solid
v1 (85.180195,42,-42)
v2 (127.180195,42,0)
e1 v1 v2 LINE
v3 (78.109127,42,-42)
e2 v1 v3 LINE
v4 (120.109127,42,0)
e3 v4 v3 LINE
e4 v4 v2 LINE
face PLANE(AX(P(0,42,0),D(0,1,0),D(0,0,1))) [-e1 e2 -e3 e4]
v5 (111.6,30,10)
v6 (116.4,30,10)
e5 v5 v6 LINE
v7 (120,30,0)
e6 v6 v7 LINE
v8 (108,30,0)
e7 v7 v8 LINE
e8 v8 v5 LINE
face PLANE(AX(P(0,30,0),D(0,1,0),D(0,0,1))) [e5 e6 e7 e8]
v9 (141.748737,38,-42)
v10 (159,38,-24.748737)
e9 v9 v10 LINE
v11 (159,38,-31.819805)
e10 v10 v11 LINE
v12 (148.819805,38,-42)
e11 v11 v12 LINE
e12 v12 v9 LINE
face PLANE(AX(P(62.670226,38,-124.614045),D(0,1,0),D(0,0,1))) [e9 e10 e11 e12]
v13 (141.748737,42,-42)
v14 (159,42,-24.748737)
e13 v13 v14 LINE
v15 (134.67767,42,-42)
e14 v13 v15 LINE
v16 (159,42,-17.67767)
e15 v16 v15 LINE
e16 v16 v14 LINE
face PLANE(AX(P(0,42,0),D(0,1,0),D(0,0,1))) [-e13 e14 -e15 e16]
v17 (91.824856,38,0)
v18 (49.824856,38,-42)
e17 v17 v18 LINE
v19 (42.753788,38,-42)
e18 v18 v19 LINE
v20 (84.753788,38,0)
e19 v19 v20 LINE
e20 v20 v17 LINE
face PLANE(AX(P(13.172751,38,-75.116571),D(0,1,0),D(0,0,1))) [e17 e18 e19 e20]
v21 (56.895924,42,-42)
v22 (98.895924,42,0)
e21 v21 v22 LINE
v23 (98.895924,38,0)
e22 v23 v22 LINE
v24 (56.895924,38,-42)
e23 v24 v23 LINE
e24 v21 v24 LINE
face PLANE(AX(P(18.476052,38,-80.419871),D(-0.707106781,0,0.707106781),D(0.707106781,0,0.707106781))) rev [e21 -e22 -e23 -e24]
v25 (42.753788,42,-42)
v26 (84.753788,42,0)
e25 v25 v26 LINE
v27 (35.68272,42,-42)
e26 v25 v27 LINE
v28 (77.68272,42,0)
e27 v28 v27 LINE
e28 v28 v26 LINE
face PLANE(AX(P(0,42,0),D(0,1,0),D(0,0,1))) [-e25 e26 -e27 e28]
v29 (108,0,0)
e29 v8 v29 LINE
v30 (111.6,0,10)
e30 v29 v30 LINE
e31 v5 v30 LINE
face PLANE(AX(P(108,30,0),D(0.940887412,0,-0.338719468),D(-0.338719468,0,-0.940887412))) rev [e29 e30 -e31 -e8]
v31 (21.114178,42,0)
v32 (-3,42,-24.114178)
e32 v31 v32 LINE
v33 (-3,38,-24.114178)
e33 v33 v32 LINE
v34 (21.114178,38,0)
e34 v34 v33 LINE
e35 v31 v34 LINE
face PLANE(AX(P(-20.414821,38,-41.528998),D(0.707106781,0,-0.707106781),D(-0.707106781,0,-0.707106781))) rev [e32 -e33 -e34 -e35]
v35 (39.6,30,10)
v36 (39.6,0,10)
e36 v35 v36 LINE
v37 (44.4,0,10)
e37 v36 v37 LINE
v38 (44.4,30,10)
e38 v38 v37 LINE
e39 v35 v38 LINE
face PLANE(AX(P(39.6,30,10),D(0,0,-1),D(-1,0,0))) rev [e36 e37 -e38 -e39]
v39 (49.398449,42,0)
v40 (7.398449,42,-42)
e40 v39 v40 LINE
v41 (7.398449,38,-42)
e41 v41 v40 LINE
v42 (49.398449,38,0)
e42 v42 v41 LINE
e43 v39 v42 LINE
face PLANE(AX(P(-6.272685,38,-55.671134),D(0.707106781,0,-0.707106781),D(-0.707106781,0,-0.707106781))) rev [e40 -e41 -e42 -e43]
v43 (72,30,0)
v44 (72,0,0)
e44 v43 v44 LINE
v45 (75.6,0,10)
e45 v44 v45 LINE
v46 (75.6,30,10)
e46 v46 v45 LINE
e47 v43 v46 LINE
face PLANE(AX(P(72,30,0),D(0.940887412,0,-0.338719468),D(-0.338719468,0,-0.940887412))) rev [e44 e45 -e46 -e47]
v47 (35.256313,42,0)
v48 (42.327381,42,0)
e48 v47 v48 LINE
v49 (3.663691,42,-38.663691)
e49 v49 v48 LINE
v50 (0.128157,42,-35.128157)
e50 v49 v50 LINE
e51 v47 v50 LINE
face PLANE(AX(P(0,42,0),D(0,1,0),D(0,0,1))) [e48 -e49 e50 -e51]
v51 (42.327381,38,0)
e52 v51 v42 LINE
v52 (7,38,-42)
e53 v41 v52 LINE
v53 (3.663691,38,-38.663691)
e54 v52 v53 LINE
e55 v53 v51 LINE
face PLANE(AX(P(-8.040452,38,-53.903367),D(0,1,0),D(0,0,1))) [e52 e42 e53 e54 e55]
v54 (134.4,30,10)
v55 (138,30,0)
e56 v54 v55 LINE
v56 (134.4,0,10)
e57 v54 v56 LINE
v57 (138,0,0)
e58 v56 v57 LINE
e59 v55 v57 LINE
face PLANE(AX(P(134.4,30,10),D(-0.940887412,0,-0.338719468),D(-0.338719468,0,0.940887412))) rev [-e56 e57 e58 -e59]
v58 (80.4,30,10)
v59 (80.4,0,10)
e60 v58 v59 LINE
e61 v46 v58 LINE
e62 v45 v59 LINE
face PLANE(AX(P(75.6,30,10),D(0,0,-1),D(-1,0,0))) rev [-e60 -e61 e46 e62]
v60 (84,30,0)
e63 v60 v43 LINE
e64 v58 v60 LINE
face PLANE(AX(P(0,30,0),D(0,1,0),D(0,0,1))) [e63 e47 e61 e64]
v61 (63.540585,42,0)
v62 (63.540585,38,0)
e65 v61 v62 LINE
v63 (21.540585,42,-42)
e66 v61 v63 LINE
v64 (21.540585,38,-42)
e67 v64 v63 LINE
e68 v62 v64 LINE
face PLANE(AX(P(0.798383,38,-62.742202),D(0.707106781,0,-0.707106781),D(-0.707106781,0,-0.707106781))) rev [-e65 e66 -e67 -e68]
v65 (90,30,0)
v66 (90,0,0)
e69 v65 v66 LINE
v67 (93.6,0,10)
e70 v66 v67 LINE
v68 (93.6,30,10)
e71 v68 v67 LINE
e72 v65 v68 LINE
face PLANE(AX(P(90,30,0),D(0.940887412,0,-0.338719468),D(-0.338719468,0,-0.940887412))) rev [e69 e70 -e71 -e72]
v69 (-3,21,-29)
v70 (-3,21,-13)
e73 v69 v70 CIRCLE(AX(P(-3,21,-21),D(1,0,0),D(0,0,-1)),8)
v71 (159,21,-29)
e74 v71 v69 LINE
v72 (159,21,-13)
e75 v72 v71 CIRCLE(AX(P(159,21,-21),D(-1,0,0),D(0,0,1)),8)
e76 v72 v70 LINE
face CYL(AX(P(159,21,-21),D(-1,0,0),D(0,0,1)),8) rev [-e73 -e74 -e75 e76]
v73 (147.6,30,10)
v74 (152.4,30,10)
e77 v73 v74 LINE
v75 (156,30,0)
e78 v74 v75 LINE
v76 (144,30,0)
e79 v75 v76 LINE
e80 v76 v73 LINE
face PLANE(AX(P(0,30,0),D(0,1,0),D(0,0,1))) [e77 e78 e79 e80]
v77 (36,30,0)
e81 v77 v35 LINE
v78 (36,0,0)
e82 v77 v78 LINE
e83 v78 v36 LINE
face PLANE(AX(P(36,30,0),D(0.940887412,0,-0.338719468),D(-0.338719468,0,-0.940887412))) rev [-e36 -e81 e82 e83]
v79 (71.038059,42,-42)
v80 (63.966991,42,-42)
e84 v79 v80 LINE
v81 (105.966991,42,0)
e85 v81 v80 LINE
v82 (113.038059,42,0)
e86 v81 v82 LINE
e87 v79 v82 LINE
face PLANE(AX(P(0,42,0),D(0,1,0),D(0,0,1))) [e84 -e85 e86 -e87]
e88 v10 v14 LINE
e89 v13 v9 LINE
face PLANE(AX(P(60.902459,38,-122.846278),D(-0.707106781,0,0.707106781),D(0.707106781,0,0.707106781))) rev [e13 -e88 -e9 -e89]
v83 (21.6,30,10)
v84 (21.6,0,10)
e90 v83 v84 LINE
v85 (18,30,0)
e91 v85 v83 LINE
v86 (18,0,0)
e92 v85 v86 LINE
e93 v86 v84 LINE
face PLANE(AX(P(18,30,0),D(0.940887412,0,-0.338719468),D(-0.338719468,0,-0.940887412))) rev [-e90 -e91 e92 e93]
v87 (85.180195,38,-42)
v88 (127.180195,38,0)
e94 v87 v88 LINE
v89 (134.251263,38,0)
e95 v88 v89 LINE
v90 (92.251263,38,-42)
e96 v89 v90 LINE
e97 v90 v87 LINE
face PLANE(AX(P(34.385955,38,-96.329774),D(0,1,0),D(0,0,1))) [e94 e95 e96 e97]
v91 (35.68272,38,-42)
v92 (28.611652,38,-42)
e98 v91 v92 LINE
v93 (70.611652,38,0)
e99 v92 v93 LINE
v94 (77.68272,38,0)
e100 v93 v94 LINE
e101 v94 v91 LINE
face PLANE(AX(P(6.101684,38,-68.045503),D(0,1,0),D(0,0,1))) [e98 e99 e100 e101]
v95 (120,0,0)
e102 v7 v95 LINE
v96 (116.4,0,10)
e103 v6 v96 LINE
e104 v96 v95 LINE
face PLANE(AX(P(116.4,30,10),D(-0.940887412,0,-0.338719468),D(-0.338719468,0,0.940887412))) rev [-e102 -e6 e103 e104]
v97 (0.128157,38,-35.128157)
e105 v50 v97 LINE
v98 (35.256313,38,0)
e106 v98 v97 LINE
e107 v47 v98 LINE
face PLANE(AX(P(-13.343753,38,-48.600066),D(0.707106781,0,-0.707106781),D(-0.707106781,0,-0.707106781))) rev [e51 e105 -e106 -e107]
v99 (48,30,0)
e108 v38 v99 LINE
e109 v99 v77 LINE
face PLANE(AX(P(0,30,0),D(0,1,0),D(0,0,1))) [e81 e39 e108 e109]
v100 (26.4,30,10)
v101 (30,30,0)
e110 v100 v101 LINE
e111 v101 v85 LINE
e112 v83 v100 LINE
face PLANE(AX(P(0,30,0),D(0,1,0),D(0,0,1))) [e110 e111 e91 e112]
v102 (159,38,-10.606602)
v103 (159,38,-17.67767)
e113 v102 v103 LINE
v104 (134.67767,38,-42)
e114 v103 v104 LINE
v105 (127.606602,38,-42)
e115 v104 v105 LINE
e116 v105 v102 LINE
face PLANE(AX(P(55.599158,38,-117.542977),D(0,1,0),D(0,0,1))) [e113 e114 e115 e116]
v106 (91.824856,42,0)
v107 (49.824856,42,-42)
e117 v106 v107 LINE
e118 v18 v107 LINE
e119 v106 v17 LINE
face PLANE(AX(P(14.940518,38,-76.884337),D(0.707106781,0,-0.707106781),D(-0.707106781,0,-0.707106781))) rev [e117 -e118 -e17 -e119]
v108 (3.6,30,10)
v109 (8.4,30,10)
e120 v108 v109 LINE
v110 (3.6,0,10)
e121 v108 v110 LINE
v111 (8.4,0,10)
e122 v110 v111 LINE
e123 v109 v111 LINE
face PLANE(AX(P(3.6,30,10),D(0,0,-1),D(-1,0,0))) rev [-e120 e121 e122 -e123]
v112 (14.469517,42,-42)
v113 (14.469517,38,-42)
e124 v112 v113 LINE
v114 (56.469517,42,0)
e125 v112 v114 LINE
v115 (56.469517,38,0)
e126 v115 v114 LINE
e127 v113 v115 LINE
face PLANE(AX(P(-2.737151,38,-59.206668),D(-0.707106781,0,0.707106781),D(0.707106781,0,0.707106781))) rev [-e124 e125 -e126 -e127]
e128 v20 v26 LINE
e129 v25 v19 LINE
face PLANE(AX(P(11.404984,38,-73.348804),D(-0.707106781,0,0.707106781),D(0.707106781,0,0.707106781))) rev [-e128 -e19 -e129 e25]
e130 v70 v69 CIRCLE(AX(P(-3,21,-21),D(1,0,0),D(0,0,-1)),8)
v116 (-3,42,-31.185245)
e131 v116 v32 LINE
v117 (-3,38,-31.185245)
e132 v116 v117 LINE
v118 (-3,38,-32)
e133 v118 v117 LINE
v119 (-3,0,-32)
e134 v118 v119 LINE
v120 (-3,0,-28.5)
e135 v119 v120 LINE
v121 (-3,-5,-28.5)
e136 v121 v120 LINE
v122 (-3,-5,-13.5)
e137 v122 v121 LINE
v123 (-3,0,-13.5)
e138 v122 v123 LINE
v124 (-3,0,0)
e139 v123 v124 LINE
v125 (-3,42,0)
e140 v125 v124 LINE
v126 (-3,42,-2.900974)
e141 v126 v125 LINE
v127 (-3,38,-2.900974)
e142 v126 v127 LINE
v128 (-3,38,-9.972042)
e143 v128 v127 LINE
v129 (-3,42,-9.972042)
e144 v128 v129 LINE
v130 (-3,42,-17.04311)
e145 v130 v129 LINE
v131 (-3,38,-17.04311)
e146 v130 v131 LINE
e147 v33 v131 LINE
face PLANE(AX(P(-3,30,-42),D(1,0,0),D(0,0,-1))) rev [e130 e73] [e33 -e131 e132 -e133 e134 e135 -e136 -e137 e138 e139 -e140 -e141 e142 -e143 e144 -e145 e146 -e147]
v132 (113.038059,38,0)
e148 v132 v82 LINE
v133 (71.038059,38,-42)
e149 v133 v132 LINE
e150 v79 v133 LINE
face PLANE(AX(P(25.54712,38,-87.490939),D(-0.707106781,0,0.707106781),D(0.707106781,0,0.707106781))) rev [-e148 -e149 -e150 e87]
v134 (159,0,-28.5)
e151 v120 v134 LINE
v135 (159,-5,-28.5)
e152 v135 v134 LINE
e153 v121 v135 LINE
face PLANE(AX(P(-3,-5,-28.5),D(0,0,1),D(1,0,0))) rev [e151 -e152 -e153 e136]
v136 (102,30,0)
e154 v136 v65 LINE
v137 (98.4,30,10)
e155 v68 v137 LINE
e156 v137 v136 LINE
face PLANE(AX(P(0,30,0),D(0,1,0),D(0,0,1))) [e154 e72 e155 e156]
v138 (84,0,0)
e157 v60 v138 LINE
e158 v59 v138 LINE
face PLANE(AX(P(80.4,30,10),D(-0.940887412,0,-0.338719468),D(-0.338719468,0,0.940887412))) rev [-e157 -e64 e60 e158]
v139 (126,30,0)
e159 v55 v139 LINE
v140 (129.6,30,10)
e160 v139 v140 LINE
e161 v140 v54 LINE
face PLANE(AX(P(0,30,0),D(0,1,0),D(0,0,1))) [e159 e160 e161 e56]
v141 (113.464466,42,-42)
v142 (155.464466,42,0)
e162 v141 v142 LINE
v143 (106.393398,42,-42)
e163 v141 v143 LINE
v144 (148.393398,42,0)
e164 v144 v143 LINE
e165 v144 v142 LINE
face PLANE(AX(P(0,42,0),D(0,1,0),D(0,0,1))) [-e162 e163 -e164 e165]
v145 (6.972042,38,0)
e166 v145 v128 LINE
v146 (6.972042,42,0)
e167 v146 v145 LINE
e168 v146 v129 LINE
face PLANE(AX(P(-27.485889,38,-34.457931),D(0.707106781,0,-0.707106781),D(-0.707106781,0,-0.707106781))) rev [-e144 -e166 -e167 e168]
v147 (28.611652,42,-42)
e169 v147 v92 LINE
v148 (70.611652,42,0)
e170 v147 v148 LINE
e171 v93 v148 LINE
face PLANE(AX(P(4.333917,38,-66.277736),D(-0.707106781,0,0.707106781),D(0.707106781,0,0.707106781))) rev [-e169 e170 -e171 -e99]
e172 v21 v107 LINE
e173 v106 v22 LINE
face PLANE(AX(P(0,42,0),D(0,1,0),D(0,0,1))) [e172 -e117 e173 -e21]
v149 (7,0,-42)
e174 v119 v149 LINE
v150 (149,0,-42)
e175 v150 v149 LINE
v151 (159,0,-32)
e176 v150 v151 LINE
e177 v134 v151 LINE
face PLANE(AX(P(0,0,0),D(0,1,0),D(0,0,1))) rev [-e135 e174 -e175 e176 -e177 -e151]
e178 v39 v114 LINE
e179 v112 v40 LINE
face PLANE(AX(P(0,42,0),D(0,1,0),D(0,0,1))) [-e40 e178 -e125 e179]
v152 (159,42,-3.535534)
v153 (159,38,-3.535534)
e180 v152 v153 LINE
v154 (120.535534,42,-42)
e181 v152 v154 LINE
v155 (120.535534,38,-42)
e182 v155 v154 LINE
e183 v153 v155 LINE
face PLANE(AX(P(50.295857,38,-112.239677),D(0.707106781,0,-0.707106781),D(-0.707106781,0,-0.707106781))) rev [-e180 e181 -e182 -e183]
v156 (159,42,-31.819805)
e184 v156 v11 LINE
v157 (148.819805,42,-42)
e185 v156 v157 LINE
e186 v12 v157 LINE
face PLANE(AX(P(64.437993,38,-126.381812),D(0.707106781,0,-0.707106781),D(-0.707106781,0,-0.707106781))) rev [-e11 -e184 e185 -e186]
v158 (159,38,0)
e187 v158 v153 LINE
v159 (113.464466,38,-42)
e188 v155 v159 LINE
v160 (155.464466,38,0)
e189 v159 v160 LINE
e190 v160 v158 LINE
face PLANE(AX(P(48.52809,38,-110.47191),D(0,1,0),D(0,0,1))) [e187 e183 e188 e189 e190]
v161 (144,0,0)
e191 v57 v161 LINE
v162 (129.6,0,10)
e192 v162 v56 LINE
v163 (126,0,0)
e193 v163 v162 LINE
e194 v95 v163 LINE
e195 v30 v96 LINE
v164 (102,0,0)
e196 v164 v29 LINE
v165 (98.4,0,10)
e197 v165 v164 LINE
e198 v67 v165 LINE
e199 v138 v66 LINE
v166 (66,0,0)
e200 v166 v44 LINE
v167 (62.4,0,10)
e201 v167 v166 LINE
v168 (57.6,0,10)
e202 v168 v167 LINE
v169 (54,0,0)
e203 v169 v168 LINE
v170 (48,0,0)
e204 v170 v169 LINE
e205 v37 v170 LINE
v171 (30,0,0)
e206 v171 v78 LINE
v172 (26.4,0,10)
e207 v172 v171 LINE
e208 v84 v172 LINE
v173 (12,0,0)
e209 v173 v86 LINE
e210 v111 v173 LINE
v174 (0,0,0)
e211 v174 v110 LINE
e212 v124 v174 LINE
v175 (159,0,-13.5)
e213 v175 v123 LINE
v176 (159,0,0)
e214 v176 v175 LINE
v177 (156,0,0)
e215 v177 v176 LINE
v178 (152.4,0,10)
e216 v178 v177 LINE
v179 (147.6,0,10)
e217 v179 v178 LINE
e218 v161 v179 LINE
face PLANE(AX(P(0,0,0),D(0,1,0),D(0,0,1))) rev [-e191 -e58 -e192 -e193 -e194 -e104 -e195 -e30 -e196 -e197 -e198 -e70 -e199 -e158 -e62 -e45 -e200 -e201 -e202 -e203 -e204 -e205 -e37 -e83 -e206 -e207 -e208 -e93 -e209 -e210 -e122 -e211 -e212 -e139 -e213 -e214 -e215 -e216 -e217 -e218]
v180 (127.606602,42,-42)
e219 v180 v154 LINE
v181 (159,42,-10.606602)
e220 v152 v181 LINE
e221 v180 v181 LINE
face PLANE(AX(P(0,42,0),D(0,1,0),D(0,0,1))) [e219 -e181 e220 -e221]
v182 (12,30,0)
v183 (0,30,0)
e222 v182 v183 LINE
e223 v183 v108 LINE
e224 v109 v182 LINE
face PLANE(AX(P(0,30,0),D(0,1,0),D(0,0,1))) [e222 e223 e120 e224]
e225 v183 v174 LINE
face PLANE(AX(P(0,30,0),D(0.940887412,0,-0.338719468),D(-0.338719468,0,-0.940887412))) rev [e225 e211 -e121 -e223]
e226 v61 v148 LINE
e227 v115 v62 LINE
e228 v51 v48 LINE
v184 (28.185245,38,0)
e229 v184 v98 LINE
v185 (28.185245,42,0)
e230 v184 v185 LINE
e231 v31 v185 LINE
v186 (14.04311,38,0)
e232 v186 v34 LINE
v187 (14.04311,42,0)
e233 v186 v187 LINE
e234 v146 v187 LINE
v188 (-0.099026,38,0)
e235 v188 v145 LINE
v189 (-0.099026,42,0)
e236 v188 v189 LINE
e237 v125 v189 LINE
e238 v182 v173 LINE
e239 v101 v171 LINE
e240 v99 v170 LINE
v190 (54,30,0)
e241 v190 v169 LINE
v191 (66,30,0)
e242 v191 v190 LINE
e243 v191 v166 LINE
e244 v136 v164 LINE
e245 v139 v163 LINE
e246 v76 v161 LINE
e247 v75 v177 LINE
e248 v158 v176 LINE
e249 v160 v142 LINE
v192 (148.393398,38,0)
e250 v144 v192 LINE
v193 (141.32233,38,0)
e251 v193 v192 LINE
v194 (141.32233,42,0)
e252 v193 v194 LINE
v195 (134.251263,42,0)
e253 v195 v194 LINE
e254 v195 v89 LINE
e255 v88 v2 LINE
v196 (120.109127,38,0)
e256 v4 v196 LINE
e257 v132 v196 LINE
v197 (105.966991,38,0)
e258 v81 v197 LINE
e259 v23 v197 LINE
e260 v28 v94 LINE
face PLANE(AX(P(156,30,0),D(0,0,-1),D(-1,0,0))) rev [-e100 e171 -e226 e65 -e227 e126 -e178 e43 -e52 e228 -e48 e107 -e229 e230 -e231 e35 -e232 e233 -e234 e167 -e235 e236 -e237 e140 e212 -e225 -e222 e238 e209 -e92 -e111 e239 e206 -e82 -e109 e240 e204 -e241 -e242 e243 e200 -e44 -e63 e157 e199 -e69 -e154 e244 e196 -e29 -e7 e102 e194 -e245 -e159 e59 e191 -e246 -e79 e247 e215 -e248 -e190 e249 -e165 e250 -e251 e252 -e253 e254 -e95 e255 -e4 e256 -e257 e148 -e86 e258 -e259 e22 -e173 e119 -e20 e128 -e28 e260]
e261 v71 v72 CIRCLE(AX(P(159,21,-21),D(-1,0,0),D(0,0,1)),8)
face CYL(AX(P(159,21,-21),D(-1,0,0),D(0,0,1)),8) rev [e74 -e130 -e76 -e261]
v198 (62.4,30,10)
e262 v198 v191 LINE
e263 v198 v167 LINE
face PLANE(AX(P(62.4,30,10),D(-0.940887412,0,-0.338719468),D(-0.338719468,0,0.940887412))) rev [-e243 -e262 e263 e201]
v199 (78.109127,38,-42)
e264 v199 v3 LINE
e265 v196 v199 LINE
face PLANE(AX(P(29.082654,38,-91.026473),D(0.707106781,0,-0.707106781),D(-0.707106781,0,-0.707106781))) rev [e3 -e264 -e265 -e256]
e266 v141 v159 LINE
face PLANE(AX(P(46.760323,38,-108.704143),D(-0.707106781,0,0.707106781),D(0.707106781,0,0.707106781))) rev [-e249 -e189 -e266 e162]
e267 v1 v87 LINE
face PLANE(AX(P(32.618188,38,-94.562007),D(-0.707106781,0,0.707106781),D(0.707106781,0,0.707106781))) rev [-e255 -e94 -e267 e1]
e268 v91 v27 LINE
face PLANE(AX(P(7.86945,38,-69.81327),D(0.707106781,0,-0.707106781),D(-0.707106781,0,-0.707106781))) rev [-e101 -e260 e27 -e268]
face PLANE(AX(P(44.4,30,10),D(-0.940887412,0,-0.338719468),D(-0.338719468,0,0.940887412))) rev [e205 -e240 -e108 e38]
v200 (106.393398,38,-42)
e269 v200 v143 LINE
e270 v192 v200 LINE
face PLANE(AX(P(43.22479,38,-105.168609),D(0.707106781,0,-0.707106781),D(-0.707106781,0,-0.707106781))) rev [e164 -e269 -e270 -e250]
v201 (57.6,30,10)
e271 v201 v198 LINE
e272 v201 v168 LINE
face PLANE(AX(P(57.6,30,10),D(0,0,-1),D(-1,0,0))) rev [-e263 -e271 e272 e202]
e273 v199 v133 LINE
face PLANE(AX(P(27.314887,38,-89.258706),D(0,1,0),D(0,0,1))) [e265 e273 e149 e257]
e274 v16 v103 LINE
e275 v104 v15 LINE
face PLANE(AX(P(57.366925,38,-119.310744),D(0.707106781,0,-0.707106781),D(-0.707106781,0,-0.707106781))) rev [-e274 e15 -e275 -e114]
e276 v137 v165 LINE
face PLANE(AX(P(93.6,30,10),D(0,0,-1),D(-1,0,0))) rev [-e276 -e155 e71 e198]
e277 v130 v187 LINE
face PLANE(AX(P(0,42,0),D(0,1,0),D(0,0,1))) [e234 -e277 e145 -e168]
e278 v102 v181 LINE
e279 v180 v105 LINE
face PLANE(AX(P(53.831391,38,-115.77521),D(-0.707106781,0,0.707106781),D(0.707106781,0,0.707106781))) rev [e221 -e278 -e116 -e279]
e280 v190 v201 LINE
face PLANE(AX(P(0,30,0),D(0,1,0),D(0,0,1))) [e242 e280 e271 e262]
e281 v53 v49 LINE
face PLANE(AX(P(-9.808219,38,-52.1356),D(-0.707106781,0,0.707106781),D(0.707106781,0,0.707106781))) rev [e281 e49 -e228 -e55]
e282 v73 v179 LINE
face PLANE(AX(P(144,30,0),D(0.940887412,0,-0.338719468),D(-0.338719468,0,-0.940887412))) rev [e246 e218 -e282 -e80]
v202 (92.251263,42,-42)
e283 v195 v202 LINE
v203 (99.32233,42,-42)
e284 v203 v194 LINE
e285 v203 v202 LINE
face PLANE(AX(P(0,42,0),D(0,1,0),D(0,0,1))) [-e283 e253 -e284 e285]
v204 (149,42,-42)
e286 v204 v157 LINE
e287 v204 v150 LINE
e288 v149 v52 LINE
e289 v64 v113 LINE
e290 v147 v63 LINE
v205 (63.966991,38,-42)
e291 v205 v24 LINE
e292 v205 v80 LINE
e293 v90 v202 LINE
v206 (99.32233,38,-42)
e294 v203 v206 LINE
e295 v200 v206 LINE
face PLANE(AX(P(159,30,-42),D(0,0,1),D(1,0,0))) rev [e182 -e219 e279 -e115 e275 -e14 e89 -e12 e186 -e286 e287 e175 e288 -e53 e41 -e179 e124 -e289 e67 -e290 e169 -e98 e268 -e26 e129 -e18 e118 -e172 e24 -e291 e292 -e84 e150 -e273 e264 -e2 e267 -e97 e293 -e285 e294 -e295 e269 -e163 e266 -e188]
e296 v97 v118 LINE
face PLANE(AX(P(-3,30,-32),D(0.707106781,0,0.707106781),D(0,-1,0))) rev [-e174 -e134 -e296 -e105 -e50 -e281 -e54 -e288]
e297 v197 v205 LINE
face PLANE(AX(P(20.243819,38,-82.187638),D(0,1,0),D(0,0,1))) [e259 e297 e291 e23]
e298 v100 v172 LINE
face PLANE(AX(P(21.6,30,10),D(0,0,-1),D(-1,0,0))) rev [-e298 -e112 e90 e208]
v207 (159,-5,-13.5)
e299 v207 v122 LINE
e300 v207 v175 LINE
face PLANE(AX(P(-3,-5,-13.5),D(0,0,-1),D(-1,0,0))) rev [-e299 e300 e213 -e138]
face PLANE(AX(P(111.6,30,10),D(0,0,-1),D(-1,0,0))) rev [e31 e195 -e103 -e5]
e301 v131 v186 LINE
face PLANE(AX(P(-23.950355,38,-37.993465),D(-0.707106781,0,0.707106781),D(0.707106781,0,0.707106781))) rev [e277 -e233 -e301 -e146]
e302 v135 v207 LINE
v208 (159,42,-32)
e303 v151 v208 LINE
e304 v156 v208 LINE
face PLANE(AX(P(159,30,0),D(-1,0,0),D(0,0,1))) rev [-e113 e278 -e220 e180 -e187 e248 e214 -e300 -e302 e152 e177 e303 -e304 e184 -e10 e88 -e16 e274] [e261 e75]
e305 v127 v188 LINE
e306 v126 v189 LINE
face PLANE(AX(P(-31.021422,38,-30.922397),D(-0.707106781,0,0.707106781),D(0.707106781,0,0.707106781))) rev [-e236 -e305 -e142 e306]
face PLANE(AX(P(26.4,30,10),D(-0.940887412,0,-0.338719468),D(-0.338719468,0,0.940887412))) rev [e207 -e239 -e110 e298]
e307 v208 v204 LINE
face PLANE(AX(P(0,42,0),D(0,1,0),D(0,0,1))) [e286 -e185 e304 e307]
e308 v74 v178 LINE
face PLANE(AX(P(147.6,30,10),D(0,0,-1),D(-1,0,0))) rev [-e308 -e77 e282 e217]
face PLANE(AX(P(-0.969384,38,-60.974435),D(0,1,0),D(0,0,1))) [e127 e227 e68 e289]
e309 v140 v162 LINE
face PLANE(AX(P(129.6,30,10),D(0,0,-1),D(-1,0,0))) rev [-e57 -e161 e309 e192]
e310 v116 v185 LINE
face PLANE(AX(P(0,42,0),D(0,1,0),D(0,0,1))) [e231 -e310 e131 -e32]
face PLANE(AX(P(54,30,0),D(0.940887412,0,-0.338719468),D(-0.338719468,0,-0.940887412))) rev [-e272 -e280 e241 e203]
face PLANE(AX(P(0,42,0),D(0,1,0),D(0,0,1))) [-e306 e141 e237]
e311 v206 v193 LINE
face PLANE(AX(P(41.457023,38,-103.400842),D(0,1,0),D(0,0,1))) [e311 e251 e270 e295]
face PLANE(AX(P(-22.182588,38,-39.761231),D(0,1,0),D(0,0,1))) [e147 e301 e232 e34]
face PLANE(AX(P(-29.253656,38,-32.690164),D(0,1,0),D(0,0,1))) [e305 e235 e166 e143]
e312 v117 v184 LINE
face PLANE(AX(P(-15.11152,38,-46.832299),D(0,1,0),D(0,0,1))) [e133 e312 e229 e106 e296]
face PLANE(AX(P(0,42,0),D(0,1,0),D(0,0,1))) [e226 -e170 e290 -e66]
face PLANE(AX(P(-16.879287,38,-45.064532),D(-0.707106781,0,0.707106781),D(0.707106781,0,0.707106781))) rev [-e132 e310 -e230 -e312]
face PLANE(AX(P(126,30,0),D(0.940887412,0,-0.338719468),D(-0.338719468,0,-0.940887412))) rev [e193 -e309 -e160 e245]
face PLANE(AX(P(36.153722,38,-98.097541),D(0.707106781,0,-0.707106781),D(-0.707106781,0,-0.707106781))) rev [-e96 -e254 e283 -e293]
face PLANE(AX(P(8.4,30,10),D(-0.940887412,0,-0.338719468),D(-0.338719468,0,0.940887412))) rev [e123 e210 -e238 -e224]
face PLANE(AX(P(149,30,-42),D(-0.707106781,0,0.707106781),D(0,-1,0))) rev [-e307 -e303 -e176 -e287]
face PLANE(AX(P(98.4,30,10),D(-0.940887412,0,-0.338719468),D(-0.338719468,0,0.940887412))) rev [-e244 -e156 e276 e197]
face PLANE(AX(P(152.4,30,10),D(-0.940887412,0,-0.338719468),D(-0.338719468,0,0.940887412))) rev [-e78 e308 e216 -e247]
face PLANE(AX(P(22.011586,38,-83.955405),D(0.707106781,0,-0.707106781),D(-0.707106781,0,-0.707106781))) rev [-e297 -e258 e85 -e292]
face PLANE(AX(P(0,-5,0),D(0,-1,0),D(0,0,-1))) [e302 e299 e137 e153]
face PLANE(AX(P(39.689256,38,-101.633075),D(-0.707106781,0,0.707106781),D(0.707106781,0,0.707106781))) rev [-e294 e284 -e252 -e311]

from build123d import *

# Parameters (mm, degrees)
BOSS_EXTRUDE1_DEPTH     = 30
SKETCH6_W               = 162
SKETCH6_H               = 42
BOSS_EXTRUDE2_DEPTH     = 12
CUT_EXTRUDE1_DEPTH      = 173.545646135
CUT_EXTRUDE1_DEPTH_BACK = 173.545646135
SKETCH7_R               = 8
SKETCH10_W              = 162
SKETCH10_H              = 15
BOSS_EXTRUDE3_DEPTH     = 5
CUT_EXTRUDE3_DEPTH      = 4
CHAMFER1_SIZE           = 10


with BuildPart() as part:
    # Sketch1 → Boss-Extrude1 (new body)
    with BuildSketch(Plane(origin=(0, 0, 0), x_dir=(1, 0, 0), z_dir=(0, 1, 0))):
        Polygon((0, 0), (3.6, -10), (8.4, -10), (12, 0), (18, 0), (21.6, -10), (26.4, -10), (30, 0), (36, 0), (39.6, -10), (44.4, -10), (48, 0), (54, 0), (57.6, -10), (62.4, -10), (66, 0), (72, 0), (75.6, -10), (80.4, -10), (84, 0), (90, 0), (93.6, -10), (98.4, -10), (102, 0), (108, 0), (111.6, -10), (116.4, -10), (120, 0), (126, 0), (129.6, -10), (134.4, -10), (138, 0), (144, 0), (147.6, -10), (152.4, -10), (156, 0), (159, 0), (159, 42), (-3, 42), (-3, 0), align=None)
    extrude(amount=BOSS_EXTRUDE1_DEPTH)

    # Sketch6 → Boss-Extrude2 (add)
    with BuildSketch(Plane(origin=(0, 30, 0), x_dir=(1, 0, 0), z_dir=(0, 1, 0))):
        with Locations((78, 21)):
            Rectangle(SKETCH6_W, SKETCH6_H)
    extrude(amount=BOSS_EXTRUDE2_DEPTH)

    # Sketch7 → Cut-Extrude1 (cut, two sides: drawn at the far end of the back side and taken through both)
    with BuildSketch(Plane.ZY.offset(3).offset(-CUT_EXTRUDE1_DEPTH_BACK)):
        with Locations((-21, 21)):
            Circle(SKETCH7_R)
    extrude(amount=CUT_EXTRUDE1_DEPTH + CUT_EXTRUDE1_DEPTH_BACK, mode=Mode.SUBTRACT)

    # Sketch10 → Boss-Extrude3 (add)
    with BuildSketch(Plane.XZ):
        with Locations((78, -21)):
            Rectangle(SKETCH10_W, SKETCH10_H)
    extrude(amount=BOSS_EXTRUDE3_DEPTH)

    # Sketch12 → Cut-Extrude3 (cut)
    with BuildSketch(Plane(origin=(0, 42, 0), x_dir=(1, 0, 0), z_dir=(0, 1, 0))):
        with BuildLine():
            Line((50.295857363, 112.239676543), (223.712429664, -61.176895758))
            ThreePointArc((223.712429664, -61.176895758), (223.712429664, -64.712429664), (220.176895758, -64.712429664))
            Line((220.176895758, -64.712429664), (46.760323457, 108.704142637))
            ThreePointArc((46.760323457, 108.704142637), (46.760323457, 112.239676543), (50.295857363, 112.239676543))
        make_face()
        with BuildLine():
            Line((53.831391269, 115.775210449), (227.24796357, -57.641361852))
            ThreePointArc((227.24796357, -57.641361852), (230.783497476, -57.641361852), (230.783497476, -54.105827946))
            Line((230.783497476, -54.105827946), (57.366925175, 119.310744355))
            ThreePointArc((57.366925175, 119.310744355), (53.831391269, 119.310744355), (53.831391269, 115.775210449))
        make_face()
        with BuildLine():
            Line((60.902459081, 122.846278261), (234.319031382, -50.57029404))
            ThreePointArc((234.319031382, -50.57029404), (237.854565288, -50.57029404), (237.854565288, -47.034760134))
            Line((237.854565288, -47.034760134), (64.437992987, 126.381812167))
            ThreePointArc((64.437992987, 126.381812167), (60.902459081, 126.381812167), (60.902459081, 122.846278261))
        make_face()
        with BuildLine():
            Line((67.973526893, 129.917346072), (241.390099194, -43.499226229))
            ThreePointArc((241.390099194, -43.499226229), (244.9256331, -43.499226229), (244.9256331, -39.963692323))
            Line((244.9256331, -39.963692323), (71.509060799, 133.452879978))
            ThreePointArc((71.509060799, 133.452879978), (67.973526893, 133.452879978), (67.973526893, 129.917346072))
        make_face()
        with BuildLine():
            Line((39.689255645, 101.633074825), (213.105827946, -71.783497476))
            ThreePointArc((213.105827946, -71.783497476), (216.641361852, -71.783497476), (216.641361852, -68.24796357))
            Line((216.641361852, -68.24796357), (43.224789551, 105.168608731))
            ThreePointArc((43.224789551, 105.168608731), (39.689255645, 105.168608731), (39.689255645, 101.633074825))
        make_face()
        with BuildLine():
            Line((32.618187833, 94.562007013), (206.034760134, -78.854565288))
            ThreePointArc((206.034760134, -78.854565288), (209.57029404, -78.854565288), (209.57029404, -75.319031382))
            Line((209.57029404, -75.319031382), (36.153721739, 98.097540919))
            ThreePointArc((36.153721739, 98.097540919), (32.618187833, 98.097540919), (32.618187833, 94.562007013))
        make_face()
        with BuildLine():
            Line((25.547120022, 87.490939201), (198.963692323, -85.9256331))
            ThreePointArc((198.963692323, -85.9256331), (202.499226229, -85.9256331), (202.499226229, -82.390099194))
            Line((202.499226229, -82.390099194), (29.082653928, 91.026473107))
            ThreePointArc((29.082653928, 91.026473107), (25.547120022, 91.026473107), (25.547120022, 87.490939201))
        make_face()
        with BuildLine():
            Line((18.47605221, 80.419871389), (191.892624511, -92.996700912))
            ThreePointArc((191.892624511, -92.996700912), (195.428158417, -92.996700912), (195.428158417, -89.461167006))
            Line((195.428158417, -89.461167006), (22.011586116, 83.955405295))
            ThreePointArc((22.011586116, 83.955405295), (18.47605221, 83.955405295), (18.47605221, 80.419871389))
        make_face()
        with BuildLine():
            Line((11.404984398, 73.348803578), (184.821556699, -100.067768723))
            ThreePointArc((184.821556699, -100.067768723), (188.357090605, -100.067768723), (188.357090605, -96.532234817))
            Line((188.357090605, -96.532234817), (14.940518304, 76.884337483))
            ThreePointArc((14.940518304, 76.884337483), (11.404984398, 76.884337483), (11.404984398, 73.348803578))
        make_face()
        with BuildLine():
            Line((4.333916586, 66.277735766), (177.750488887, -107.138836535))
            ThreePointArc((177.750488887, -107.138836535), (181.286022793, -107.138836535), (181.286022793, -103.603302629))
            Line((181.286022793, -103.603302629), (7.869450492, 69.813269672))
            ThreePointArc((7.869450492, 69.813269672), (4.333916586, 69.813269672), (4.333916586, 66.277735766))
        make_face()
        with BuildLine():
            Line((-2.737151226, 59.206667954), (170.679421075, -114.209904347))
            ThreePointArc((170.679421075, -114.209904347), (174.214954981, -114.209904347), (174.214954981, -110.674370441))
            Line((174.214954981, -110.674370441), (0.79838268, 62.74220186))
            ThreePointArc((0.79838268, 62.74220186), (-2.737151226, 62.74220186), (-2.737151226, 59.206667954))
        make_face()
        with BuildLine():
            Line((-9.808219038, 52.135600142), (163.608353263, -121.280972159))
            ThreePointArc((163.608353263, -121.280972159), (167.143887169, -121.280972159), (167.143887169, -117.745438253))
            Line((167.143887169, -117.745438253), (-6.272685132, 55.671134048))
            ThreePointArc((-6.272685132, 55.671134048), (-9.808219038, 55.671134048), (-9.808219038, 52.135600142))
        make_face()
        with BuildLine():
            Line((-16.87928685, 45.06453233), (156.537285451, -128.352039971))
            ThreePointArc((156.537285451, -128.352039971), (160.072819357, -128.352039971), (160.072819357, -124.816506065))
            Line((160.072819357, -124.816506065), (-13.343752944, 48.600066236))
            ThreePointArc((-13.343752944, 48.600066236), (-16.87928685, 48.600066236), (-16.87928685, 45.06453233))
        make_face()
        with BuildLine():
            Line((-23.950354661, 37.993464518), (149.46621764, -135.423107783))
            ThreePointArc((149.46621764, -135.423107783), (153.001751545, -135.423107783), (153.001751545, -131.887573877))
            Line((153.001751545, -131.887573877), (-20.414820756, 41.528998424))
            ThreePointArc((-20.414820756, 41.528998424), (-23.950354661, 41.528998424), (-23.950354661, 37.993464518))
        make_face()
        with BuildLine():
            Line((-31.021422473, 30.922396706), (142.395149828, -142.494175595))
            ThreePointArc((142.395149828, -142.494175595), (145.930683734, -142.494175595), (145.930683734, -138.958641689))
            Line((145.930683734, -138.958641689), (-27.485888567, 34.457930612))
            ThreePointArc((-27.485888567, 34.457930612), (-31.021422473, 34.457930612), (-31.021422473, 30.922396706))
        make_face()
        with BuildLine():
            Line((-38.092490285, 23.851328894), (135.324082016, -149.565243406))
            ThreePointArc((135.324082016, -149.565243406), (138.859615922, -149.565243406), (138.859615922, -146.029709501))
            Line((138.859615922, -146.029709501), (-34.556956379, 27.3868628))
            ThreePointArc((-34.556956379, 27.3868628), (-38.092490285, 27.3868628), (-38.092490285, 23.851328894))
        make_face()
    extrude(amount=-CUT_EXTRUDE3_DEPTH, mode=Mode.SUBTRACT)

    # Chamfer1
    chamfer1_edges = [part.edges().sort_by_distance(p)[0] for p in [
        (-3, 21, -42),
        (159, 19, -42),
    ]]
    chamfer(chamfer1_edges, length=CHAMFER1_SIZE)


solid = part.part
